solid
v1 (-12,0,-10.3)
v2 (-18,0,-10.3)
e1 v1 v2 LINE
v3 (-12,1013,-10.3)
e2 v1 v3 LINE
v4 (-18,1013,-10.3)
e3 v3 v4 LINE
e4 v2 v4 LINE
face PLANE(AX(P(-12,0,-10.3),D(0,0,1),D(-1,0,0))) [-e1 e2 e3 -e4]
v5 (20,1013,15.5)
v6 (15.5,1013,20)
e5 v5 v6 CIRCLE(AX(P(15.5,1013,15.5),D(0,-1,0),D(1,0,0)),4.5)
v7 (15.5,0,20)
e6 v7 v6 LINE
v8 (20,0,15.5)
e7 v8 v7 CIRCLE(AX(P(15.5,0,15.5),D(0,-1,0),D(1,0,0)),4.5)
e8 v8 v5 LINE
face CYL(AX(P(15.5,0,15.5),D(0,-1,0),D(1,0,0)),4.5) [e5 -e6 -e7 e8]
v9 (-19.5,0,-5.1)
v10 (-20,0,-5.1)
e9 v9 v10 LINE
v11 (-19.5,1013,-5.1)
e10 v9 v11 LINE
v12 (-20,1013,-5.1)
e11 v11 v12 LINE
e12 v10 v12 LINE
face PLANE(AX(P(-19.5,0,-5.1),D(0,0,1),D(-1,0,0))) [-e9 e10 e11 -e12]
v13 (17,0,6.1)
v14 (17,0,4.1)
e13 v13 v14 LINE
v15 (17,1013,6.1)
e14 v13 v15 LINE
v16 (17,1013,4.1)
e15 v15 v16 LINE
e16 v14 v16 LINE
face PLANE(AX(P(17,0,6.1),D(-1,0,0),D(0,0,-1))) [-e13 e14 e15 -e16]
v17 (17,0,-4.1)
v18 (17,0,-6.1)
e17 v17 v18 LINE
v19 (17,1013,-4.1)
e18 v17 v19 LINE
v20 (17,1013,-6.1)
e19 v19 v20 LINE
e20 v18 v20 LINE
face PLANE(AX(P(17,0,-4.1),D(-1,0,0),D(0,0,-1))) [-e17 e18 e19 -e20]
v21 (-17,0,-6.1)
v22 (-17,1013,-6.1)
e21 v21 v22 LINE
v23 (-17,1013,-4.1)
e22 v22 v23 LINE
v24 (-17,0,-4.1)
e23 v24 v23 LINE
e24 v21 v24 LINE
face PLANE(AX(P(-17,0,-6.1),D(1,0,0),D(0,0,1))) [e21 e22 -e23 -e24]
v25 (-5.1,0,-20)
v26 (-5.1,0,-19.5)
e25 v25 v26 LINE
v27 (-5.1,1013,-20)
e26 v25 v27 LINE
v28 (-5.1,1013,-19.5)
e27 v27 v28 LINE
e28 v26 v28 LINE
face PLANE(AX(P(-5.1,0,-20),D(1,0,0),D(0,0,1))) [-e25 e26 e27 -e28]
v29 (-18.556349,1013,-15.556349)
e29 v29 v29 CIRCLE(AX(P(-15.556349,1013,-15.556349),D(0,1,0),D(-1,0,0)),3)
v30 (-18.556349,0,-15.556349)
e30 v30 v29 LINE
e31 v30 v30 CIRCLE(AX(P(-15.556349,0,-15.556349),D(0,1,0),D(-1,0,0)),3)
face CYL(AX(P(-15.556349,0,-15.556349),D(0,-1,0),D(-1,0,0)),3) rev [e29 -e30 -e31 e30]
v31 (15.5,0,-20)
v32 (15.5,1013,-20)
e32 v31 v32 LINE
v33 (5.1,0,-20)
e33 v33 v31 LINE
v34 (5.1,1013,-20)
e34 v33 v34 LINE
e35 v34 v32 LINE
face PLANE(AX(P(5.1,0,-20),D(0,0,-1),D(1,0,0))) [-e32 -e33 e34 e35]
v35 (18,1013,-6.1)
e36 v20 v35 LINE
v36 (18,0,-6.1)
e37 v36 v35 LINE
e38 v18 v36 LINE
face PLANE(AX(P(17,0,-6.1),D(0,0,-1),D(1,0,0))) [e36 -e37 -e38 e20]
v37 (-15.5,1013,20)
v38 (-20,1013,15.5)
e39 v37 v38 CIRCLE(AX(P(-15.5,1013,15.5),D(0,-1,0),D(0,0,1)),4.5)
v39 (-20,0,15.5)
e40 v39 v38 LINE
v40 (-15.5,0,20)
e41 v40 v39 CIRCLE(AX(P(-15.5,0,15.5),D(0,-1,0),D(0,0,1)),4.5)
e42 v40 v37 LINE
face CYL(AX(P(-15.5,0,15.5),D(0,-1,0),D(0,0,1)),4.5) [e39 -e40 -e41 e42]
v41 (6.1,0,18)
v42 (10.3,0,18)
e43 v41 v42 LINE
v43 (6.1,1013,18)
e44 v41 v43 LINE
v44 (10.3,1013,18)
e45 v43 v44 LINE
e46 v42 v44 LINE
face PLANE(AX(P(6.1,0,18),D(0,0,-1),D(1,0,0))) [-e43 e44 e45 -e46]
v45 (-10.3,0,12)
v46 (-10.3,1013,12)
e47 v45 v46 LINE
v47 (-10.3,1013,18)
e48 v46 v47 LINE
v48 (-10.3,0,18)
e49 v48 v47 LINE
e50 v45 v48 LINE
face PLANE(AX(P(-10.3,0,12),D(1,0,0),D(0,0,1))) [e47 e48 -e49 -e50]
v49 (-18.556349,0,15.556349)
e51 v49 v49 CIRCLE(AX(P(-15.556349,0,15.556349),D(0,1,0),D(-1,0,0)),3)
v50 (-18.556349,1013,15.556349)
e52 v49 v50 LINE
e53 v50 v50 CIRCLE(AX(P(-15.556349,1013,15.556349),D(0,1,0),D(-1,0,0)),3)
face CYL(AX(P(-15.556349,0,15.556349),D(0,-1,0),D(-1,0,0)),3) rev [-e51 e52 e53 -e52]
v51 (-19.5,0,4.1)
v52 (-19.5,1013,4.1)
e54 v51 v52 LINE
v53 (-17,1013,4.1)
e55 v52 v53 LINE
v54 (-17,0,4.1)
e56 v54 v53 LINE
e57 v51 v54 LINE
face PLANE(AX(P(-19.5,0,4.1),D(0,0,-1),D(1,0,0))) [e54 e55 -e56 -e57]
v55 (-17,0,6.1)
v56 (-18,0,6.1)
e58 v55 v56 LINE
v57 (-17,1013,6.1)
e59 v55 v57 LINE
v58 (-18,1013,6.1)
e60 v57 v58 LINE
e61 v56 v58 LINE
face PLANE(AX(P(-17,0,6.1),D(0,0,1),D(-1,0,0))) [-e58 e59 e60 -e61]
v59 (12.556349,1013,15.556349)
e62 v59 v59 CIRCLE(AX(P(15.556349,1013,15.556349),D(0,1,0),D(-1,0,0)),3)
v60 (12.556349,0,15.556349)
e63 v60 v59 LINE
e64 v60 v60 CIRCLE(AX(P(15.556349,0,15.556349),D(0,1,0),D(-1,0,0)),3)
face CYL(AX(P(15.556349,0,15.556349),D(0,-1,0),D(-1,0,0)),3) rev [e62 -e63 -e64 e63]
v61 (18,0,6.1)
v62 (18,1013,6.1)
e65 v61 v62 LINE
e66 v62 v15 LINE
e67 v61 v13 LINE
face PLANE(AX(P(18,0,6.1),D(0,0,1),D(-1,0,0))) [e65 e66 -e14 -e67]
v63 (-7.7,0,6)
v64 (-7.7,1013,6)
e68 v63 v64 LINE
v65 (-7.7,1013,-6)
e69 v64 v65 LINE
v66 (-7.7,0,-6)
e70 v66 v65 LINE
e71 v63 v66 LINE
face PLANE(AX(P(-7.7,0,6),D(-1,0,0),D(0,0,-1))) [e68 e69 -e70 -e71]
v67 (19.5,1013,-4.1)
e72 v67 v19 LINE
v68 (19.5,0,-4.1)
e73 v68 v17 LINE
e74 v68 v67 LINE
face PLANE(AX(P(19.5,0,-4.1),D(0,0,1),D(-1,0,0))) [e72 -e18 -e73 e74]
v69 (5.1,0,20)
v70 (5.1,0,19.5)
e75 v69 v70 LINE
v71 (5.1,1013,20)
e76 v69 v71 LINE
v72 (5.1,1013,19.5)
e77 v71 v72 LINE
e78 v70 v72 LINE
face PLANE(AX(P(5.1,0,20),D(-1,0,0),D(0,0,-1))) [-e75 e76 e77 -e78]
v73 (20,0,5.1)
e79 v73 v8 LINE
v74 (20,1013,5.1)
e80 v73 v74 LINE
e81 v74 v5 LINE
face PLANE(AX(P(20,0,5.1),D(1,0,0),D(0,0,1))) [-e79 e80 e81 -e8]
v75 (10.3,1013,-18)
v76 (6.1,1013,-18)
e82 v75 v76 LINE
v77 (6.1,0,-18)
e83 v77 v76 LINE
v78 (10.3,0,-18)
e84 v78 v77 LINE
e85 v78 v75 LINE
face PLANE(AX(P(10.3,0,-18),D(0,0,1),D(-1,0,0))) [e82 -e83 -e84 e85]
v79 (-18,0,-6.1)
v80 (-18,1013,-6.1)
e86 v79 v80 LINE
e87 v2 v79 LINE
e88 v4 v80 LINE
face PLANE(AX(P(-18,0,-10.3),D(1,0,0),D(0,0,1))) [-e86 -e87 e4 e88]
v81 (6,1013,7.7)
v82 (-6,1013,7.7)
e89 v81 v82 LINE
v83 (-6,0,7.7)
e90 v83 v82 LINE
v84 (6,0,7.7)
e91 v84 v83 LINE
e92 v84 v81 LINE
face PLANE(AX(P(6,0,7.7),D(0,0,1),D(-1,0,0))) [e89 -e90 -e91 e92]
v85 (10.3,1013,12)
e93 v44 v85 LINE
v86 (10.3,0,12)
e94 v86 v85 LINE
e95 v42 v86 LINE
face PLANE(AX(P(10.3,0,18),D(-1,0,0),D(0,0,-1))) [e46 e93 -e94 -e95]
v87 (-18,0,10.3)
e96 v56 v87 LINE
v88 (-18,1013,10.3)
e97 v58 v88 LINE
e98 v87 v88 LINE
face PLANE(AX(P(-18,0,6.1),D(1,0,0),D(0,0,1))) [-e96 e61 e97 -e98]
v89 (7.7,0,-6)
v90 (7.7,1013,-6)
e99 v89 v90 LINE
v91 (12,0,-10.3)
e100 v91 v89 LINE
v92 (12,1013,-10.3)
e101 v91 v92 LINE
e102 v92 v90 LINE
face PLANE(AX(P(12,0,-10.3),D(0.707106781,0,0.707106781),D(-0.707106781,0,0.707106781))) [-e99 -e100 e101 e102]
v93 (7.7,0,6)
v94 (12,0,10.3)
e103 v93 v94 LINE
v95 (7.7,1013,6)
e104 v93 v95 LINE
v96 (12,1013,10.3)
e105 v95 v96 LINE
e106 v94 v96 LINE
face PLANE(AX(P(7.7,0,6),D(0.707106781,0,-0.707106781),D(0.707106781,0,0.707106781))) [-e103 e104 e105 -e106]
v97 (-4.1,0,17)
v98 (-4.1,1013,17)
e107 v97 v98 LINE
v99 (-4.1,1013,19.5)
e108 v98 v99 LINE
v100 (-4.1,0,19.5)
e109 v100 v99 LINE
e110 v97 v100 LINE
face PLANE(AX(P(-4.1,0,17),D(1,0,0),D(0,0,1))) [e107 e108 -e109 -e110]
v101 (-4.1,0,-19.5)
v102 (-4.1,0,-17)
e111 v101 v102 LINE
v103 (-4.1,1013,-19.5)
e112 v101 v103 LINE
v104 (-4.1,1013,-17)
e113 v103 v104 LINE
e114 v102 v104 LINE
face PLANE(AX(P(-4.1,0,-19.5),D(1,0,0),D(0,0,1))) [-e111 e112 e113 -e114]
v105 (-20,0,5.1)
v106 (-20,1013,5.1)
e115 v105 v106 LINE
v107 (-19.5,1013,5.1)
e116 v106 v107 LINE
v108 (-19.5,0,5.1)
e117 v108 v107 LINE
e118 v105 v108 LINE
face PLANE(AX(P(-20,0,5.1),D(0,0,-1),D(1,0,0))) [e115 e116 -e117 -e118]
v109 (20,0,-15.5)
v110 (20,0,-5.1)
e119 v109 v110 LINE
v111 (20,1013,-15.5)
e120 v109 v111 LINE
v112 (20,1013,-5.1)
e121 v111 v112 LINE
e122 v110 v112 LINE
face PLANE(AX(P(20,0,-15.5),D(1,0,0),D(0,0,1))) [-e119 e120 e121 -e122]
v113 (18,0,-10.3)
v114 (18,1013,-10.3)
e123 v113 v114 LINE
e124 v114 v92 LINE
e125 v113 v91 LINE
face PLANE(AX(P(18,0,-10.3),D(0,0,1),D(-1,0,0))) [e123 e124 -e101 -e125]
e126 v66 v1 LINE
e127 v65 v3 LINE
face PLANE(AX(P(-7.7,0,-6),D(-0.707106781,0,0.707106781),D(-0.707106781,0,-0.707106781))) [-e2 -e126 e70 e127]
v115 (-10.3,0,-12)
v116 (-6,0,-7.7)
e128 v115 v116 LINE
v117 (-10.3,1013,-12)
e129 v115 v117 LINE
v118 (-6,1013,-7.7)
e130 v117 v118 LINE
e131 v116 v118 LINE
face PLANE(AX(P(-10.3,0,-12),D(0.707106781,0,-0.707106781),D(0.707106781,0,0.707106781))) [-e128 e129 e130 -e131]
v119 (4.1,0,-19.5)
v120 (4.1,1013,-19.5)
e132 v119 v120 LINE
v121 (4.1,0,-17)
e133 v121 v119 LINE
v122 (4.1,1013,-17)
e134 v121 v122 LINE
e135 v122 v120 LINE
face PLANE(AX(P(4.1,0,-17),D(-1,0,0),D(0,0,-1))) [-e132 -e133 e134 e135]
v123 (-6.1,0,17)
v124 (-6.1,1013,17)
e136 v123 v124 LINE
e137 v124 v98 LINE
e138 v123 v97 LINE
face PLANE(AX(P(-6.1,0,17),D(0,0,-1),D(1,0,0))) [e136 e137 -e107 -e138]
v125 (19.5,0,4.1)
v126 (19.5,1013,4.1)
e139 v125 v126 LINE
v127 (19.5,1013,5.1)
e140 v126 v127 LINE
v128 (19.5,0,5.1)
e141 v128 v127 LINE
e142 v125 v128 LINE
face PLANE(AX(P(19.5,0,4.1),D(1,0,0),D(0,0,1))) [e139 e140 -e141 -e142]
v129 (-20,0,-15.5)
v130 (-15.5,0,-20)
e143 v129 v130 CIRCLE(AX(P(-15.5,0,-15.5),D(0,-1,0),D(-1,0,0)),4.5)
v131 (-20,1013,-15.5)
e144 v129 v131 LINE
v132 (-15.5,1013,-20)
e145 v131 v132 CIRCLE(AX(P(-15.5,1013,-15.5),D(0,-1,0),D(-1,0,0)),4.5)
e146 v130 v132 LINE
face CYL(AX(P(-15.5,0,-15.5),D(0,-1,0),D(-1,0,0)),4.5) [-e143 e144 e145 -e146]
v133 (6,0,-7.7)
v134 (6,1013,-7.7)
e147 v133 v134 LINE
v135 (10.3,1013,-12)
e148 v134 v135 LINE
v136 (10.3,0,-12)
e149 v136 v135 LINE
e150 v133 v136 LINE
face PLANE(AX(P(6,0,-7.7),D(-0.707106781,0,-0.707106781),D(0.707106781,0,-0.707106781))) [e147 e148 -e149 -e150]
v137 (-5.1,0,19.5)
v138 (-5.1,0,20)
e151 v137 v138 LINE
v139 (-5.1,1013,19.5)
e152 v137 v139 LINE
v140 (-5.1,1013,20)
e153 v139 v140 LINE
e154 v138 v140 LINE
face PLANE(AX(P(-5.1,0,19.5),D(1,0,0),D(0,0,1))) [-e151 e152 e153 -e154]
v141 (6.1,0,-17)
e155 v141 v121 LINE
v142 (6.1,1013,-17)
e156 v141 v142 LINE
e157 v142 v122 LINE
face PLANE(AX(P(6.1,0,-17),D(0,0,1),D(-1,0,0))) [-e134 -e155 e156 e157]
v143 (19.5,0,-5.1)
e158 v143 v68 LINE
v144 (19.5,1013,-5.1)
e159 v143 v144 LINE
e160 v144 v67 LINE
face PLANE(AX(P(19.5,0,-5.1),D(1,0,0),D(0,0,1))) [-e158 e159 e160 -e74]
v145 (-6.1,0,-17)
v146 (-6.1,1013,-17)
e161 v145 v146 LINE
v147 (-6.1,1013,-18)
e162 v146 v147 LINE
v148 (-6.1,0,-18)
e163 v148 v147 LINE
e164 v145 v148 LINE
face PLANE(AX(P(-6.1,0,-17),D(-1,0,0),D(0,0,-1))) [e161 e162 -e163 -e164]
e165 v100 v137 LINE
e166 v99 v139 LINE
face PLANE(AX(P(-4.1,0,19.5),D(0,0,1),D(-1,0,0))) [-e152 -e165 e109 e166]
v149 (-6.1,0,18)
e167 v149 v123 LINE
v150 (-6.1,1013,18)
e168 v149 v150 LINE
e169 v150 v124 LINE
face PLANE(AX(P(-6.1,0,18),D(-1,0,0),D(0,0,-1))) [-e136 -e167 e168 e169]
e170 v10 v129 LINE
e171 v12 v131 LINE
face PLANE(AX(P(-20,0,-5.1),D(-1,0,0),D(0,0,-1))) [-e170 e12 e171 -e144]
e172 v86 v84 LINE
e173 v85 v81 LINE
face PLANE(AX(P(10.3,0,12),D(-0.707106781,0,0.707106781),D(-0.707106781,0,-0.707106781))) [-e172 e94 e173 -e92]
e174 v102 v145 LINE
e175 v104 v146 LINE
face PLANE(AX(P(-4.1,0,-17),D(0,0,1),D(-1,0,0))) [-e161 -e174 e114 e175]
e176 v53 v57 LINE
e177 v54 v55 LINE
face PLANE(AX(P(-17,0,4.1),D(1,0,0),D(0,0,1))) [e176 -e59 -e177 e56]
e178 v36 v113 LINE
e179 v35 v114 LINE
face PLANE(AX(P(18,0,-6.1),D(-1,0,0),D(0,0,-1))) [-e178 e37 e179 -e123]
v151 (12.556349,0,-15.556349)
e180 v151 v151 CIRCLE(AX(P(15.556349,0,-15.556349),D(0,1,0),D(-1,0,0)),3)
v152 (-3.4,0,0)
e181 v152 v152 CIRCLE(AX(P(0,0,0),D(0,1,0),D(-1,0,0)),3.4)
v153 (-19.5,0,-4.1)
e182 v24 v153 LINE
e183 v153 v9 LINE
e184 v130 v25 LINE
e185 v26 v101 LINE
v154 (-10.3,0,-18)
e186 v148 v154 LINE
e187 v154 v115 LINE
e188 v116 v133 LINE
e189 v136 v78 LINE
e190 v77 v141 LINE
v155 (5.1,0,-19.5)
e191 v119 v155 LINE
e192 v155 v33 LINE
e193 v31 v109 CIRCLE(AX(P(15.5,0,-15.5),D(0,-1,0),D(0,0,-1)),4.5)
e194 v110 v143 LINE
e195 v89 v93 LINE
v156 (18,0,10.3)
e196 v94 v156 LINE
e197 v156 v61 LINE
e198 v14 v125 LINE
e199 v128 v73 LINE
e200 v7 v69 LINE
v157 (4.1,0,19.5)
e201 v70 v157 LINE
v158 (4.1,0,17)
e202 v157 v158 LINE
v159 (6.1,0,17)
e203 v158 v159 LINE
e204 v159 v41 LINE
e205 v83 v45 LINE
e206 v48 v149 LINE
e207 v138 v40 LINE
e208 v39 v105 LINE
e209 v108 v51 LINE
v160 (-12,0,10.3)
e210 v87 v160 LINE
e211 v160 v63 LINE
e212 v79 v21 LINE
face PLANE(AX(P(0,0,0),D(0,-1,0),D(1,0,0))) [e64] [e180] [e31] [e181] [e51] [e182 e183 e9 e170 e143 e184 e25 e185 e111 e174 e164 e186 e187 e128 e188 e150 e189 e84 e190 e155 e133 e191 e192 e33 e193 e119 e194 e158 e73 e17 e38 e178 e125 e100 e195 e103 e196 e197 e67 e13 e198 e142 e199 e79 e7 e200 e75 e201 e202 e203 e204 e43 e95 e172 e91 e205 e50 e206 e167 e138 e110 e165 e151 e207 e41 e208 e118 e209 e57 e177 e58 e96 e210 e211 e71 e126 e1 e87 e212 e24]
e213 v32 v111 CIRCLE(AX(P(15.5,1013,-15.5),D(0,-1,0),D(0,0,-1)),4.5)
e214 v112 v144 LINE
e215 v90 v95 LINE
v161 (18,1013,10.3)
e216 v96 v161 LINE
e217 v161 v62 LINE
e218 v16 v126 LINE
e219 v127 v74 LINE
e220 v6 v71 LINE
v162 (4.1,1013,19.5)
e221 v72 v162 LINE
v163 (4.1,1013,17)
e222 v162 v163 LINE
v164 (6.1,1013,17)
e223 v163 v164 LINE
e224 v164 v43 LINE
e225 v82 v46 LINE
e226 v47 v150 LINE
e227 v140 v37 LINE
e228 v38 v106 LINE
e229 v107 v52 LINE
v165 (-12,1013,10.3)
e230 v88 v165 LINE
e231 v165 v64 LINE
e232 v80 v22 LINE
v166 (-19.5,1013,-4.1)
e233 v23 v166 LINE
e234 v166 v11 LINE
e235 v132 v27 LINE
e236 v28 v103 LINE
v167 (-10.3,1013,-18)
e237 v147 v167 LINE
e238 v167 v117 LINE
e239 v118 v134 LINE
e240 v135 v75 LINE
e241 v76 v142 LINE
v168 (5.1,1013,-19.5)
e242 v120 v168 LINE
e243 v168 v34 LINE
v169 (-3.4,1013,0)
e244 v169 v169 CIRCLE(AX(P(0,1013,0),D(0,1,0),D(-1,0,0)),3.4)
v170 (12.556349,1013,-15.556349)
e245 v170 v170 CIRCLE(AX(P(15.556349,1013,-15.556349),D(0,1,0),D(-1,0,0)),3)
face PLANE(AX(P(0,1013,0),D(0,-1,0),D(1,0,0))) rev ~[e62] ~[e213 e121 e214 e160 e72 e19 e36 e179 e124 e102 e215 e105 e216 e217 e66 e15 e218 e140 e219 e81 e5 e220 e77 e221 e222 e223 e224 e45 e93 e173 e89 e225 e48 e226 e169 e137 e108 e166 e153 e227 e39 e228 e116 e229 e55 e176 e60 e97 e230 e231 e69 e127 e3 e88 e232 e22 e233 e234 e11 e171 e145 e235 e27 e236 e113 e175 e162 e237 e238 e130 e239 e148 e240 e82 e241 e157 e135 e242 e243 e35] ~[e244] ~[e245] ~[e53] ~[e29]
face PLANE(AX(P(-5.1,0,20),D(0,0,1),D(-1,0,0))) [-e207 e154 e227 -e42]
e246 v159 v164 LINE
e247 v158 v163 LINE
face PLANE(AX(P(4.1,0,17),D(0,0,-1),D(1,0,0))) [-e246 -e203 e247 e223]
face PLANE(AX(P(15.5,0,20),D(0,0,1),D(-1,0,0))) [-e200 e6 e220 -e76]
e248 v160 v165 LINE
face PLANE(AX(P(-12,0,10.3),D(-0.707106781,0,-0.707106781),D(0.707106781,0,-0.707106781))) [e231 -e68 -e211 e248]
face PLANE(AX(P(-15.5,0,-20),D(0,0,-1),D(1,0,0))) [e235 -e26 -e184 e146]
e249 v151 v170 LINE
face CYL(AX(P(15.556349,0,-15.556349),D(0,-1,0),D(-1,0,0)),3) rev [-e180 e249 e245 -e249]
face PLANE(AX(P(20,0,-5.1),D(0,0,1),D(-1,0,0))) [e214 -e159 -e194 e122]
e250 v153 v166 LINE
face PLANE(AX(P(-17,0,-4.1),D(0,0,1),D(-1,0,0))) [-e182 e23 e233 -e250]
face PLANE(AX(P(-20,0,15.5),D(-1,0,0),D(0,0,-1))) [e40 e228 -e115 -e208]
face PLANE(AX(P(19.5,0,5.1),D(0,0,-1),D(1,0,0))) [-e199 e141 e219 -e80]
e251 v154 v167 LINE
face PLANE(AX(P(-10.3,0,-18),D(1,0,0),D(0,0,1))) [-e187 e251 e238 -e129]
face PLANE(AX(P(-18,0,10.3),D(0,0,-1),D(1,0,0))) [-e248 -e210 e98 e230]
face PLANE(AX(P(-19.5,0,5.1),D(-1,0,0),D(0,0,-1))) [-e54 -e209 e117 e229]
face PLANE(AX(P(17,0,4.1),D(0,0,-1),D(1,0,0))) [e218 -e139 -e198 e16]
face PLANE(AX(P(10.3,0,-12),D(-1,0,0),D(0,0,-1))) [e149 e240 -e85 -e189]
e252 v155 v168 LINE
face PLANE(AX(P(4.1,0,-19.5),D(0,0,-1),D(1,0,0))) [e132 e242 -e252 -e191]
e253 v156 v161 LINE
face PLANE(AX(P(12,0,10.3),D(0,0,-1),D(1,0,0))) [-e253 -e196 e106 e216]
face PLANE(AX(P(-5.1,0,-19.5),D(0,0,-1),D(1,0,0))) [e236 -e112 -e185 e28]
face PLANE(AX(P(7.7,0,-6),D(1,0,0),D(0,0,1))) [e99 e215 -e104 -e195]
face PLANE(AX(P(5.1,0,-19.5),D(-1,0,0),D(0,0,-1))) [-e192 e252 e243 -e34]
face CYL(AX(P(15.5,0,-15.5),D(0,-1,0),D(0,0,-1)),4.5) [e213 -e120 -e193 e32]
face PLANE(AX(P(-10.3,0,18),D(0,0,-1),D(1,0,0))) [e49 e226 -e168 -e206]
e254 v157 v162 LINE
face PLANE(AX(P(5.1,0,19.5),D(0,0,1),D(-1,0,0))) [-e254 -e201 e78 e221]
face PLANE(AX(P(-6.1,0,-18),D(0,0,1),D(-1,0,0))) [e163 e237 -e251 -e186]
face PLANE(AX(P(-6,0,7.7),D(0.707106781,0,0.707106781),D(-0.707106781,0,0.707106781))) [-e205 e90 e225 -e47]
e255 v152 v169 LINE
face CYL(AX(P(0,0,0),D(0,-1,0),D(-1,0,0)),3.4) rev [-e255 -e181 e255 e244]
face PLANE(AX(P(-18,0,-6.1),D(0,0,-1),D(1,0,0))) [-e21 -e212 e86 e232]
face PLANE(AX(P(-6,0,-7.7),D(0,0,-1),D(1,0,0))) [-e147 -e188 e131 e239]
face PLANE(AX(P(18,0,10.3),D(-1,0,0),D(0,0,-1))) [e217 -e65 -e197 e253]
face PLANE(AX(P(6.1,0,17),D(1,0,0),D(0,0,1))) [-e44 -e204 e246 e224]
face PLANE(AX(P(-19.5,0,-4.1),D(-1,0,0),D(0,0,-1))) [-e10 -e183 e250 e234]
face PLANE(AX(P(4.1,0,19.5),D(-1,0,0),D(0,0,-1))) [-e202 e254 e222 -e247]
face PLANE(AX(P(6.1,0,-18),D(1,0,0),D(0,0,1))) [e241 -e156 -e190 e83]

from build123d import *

# Parameters (mm, degrees)
SKETCH16_R     = 3.4
SKETCH16_R_2   = 3
MEMBER_1_DEPTH = 1013


with BuildPart() as part:
    # Sketch16 → Member 1 (new body)
    with BuildSketch(Plane(origin=(0, 0, 0), x_dir=(-1, 0, 0), z_dir=(0, 1, 0))):
        with BuildLine():
            Line((-5.1, 20), (-5.1, 19.5))
            Line((-5.1, 19.5), (-4.1, 19.5))
            Line((-4.1, 19.5), (-4.1, 17))
            Line((-4.1, 17), (-6.1, 17))
            Line((-6.1, 17), (-6.1, 18))
            Line((-6.1, 18), (-10.3, 18))
            Line((-10.3, 18), (-10.3, 12))
            Line((-10.3, 12), (-6, 7.7))
            Line((-6, 7.7), (6, 7.7))
            Line((6, 7.7), (10.3, 12))
            Line((10.3, 12), (10.3, 18))
            Line((10.3, 18), (6.1, 18))
            Line((6.1, 18), (6.1, 17))
            Line((6.1, 17), (4.1, 17))
            Line((4.1, 17), (4.1, 19.5))
            Line((4.1, 19.5), (5.1, 19.5))
            Line((5.1, 19.5), (5.1, 20))
            Line((5.1, 20), (15.5, 20))
            ThreePointArc((15.5, 20), (18.681980515, 18.681980515), (20, 15.5))
            Line((20, 15.5), (20, 5.1))
            Line((20, 5.1), (19.5, 5.1))
            Line((19.5, 5.1), (19.5, 4.1))
            Line((19.5, 4.1), (17, 4.1))
            Line((17, 4.1), (17, 6.1))
            Line((17, 6.1), (18, 6.1))
            Line((18, 6.1), (18, 10.3))
            Line((18, 10.3), (12, 10.3))
            Line((12, 10.3), (7.7, 6))
            Line((7.7, 6), (7.7, -6))
            Line((7.7, -6), (12, -10.3))
            Line((12, -10.3), (18, -10.3))
            Line((18, -10.3), (18, -6.1))
            Line((18, -6.1), (17, -6.1))
            Line((17, -6.1), (17, -4.1))
            Line((17, -4.1), (19.5, -4.1))
            Line((19.5, -4.1), (19.5, -5.1))
            Line((19.5, -5.1), (20, -5.1))
            Line((20, -5.1), (20, -15.5))
            ThreePointArc((20, -15.5), (18.681980515, -18.681980515), (15.5, -20))
            Line((15.5, -20), (5.1, -20))
            Line((5.1, -20), (5.1, -19.5))
            Line((5.1, -19.5), (4.1, -19.5))
            Line((4.1, -19.5), (4.1, -17))
            Line((4.1, -17), (6.1, -17))
            Line((6.1, -17), (6.1, -18))
            Line((6.1, -18), (10.3, -18))
            Line((10.3, -18), (10.3, -12))
            Line((10.3, -12), (6, -7.7))
            Line((6, -7.7), (-6, -7.7))
            Line((-6, -7.7), (-10.3, -12))
            Line((-10.3, -12), (-10.3, -18))
            Line((-10.3, -18), (-6.1, -18))
            Line((-6.1, -18), (-6.1, -17))
            Line((-6.1, -17), (-4.1, -17))
            Line((-4.1, -17), (-4.1, -19.5))
            Line((-4.1, -19.5), (-5.1, -19.5))
            Line((-5.1, -19.5), (-5.1, -20))
            Line((-5.1, -20), (-15.5, -20))
            ThreePointArc((-15.5, -20), (-18.681980515, -18.681980515), (-20, -15.5))
            Line((-20, -15.5), (-20, -5.1))
            Line((-20, -5.1), (-19.5, -5.1))
            Line((-19.5, -5.1), (-19.5, -4.1))
            Line((-19.5, -4.1), (-17, -4.1))
            Line((-17, -4.1), (-17, -6.1))
            Line((-17, -6.1), (-18, -6.1))
            Line((-18, -6.1), (-18, -10.3))
            Line((-18, -10.3), (-12, -10.3))
            Line((-12, -10.3), (-7.7, -6))
            Line((-7.7, -6), (-7.7, 6))
            Line((-7.7, 6), (-12, 10.3))
            Line((-12, 10.3), (-18, 10.3))
            Line((-18, 10.3), (-18, 6.1))
            Line((-18, 6.1), (-17, 6.1))
            Line((-17, 6.1), (-17, 4.1))
            Line((-17, 4.1), (-19.5, 4.1))
            Line((-19.5, 4.1), (-19.5, 5.1))
            Line((-19.5, 5.1), (-20, 5.1))
            Line((-20, 5.1), (-20, 15.5))
            ThreePointArc((-20, 15.5), (-18.681980515, 18.681980515), (-15.5, 20))
            Line((-15.5, 20), (-5.1, 20))
        make_face()
        Circle(SKETCH16_R, mode=Mode.SUBTRACT)
        with Locations((-15.556349186, 15.556349186)):
            Circle(SKETCH16_R_2, mode=Mode.SUBTRACT)
        with Locations((15.556349186, 15.556349186)):
            Circle(SKETCH16_R_2, mode=Mode.SUBTRACT)
        with Locations((15.556349186, -15.556349186)):
            Circle(SKETCH16_R_2, mode=Mode.SUBTRACT)
        with Locations((-15.556349186, -15.556349186)):
            Circle(SKETCH16_R_2, mode=Mode.SUBTRACT)
    extrude(amount=MEMBER_1_DEPTH)


solid = part.part
